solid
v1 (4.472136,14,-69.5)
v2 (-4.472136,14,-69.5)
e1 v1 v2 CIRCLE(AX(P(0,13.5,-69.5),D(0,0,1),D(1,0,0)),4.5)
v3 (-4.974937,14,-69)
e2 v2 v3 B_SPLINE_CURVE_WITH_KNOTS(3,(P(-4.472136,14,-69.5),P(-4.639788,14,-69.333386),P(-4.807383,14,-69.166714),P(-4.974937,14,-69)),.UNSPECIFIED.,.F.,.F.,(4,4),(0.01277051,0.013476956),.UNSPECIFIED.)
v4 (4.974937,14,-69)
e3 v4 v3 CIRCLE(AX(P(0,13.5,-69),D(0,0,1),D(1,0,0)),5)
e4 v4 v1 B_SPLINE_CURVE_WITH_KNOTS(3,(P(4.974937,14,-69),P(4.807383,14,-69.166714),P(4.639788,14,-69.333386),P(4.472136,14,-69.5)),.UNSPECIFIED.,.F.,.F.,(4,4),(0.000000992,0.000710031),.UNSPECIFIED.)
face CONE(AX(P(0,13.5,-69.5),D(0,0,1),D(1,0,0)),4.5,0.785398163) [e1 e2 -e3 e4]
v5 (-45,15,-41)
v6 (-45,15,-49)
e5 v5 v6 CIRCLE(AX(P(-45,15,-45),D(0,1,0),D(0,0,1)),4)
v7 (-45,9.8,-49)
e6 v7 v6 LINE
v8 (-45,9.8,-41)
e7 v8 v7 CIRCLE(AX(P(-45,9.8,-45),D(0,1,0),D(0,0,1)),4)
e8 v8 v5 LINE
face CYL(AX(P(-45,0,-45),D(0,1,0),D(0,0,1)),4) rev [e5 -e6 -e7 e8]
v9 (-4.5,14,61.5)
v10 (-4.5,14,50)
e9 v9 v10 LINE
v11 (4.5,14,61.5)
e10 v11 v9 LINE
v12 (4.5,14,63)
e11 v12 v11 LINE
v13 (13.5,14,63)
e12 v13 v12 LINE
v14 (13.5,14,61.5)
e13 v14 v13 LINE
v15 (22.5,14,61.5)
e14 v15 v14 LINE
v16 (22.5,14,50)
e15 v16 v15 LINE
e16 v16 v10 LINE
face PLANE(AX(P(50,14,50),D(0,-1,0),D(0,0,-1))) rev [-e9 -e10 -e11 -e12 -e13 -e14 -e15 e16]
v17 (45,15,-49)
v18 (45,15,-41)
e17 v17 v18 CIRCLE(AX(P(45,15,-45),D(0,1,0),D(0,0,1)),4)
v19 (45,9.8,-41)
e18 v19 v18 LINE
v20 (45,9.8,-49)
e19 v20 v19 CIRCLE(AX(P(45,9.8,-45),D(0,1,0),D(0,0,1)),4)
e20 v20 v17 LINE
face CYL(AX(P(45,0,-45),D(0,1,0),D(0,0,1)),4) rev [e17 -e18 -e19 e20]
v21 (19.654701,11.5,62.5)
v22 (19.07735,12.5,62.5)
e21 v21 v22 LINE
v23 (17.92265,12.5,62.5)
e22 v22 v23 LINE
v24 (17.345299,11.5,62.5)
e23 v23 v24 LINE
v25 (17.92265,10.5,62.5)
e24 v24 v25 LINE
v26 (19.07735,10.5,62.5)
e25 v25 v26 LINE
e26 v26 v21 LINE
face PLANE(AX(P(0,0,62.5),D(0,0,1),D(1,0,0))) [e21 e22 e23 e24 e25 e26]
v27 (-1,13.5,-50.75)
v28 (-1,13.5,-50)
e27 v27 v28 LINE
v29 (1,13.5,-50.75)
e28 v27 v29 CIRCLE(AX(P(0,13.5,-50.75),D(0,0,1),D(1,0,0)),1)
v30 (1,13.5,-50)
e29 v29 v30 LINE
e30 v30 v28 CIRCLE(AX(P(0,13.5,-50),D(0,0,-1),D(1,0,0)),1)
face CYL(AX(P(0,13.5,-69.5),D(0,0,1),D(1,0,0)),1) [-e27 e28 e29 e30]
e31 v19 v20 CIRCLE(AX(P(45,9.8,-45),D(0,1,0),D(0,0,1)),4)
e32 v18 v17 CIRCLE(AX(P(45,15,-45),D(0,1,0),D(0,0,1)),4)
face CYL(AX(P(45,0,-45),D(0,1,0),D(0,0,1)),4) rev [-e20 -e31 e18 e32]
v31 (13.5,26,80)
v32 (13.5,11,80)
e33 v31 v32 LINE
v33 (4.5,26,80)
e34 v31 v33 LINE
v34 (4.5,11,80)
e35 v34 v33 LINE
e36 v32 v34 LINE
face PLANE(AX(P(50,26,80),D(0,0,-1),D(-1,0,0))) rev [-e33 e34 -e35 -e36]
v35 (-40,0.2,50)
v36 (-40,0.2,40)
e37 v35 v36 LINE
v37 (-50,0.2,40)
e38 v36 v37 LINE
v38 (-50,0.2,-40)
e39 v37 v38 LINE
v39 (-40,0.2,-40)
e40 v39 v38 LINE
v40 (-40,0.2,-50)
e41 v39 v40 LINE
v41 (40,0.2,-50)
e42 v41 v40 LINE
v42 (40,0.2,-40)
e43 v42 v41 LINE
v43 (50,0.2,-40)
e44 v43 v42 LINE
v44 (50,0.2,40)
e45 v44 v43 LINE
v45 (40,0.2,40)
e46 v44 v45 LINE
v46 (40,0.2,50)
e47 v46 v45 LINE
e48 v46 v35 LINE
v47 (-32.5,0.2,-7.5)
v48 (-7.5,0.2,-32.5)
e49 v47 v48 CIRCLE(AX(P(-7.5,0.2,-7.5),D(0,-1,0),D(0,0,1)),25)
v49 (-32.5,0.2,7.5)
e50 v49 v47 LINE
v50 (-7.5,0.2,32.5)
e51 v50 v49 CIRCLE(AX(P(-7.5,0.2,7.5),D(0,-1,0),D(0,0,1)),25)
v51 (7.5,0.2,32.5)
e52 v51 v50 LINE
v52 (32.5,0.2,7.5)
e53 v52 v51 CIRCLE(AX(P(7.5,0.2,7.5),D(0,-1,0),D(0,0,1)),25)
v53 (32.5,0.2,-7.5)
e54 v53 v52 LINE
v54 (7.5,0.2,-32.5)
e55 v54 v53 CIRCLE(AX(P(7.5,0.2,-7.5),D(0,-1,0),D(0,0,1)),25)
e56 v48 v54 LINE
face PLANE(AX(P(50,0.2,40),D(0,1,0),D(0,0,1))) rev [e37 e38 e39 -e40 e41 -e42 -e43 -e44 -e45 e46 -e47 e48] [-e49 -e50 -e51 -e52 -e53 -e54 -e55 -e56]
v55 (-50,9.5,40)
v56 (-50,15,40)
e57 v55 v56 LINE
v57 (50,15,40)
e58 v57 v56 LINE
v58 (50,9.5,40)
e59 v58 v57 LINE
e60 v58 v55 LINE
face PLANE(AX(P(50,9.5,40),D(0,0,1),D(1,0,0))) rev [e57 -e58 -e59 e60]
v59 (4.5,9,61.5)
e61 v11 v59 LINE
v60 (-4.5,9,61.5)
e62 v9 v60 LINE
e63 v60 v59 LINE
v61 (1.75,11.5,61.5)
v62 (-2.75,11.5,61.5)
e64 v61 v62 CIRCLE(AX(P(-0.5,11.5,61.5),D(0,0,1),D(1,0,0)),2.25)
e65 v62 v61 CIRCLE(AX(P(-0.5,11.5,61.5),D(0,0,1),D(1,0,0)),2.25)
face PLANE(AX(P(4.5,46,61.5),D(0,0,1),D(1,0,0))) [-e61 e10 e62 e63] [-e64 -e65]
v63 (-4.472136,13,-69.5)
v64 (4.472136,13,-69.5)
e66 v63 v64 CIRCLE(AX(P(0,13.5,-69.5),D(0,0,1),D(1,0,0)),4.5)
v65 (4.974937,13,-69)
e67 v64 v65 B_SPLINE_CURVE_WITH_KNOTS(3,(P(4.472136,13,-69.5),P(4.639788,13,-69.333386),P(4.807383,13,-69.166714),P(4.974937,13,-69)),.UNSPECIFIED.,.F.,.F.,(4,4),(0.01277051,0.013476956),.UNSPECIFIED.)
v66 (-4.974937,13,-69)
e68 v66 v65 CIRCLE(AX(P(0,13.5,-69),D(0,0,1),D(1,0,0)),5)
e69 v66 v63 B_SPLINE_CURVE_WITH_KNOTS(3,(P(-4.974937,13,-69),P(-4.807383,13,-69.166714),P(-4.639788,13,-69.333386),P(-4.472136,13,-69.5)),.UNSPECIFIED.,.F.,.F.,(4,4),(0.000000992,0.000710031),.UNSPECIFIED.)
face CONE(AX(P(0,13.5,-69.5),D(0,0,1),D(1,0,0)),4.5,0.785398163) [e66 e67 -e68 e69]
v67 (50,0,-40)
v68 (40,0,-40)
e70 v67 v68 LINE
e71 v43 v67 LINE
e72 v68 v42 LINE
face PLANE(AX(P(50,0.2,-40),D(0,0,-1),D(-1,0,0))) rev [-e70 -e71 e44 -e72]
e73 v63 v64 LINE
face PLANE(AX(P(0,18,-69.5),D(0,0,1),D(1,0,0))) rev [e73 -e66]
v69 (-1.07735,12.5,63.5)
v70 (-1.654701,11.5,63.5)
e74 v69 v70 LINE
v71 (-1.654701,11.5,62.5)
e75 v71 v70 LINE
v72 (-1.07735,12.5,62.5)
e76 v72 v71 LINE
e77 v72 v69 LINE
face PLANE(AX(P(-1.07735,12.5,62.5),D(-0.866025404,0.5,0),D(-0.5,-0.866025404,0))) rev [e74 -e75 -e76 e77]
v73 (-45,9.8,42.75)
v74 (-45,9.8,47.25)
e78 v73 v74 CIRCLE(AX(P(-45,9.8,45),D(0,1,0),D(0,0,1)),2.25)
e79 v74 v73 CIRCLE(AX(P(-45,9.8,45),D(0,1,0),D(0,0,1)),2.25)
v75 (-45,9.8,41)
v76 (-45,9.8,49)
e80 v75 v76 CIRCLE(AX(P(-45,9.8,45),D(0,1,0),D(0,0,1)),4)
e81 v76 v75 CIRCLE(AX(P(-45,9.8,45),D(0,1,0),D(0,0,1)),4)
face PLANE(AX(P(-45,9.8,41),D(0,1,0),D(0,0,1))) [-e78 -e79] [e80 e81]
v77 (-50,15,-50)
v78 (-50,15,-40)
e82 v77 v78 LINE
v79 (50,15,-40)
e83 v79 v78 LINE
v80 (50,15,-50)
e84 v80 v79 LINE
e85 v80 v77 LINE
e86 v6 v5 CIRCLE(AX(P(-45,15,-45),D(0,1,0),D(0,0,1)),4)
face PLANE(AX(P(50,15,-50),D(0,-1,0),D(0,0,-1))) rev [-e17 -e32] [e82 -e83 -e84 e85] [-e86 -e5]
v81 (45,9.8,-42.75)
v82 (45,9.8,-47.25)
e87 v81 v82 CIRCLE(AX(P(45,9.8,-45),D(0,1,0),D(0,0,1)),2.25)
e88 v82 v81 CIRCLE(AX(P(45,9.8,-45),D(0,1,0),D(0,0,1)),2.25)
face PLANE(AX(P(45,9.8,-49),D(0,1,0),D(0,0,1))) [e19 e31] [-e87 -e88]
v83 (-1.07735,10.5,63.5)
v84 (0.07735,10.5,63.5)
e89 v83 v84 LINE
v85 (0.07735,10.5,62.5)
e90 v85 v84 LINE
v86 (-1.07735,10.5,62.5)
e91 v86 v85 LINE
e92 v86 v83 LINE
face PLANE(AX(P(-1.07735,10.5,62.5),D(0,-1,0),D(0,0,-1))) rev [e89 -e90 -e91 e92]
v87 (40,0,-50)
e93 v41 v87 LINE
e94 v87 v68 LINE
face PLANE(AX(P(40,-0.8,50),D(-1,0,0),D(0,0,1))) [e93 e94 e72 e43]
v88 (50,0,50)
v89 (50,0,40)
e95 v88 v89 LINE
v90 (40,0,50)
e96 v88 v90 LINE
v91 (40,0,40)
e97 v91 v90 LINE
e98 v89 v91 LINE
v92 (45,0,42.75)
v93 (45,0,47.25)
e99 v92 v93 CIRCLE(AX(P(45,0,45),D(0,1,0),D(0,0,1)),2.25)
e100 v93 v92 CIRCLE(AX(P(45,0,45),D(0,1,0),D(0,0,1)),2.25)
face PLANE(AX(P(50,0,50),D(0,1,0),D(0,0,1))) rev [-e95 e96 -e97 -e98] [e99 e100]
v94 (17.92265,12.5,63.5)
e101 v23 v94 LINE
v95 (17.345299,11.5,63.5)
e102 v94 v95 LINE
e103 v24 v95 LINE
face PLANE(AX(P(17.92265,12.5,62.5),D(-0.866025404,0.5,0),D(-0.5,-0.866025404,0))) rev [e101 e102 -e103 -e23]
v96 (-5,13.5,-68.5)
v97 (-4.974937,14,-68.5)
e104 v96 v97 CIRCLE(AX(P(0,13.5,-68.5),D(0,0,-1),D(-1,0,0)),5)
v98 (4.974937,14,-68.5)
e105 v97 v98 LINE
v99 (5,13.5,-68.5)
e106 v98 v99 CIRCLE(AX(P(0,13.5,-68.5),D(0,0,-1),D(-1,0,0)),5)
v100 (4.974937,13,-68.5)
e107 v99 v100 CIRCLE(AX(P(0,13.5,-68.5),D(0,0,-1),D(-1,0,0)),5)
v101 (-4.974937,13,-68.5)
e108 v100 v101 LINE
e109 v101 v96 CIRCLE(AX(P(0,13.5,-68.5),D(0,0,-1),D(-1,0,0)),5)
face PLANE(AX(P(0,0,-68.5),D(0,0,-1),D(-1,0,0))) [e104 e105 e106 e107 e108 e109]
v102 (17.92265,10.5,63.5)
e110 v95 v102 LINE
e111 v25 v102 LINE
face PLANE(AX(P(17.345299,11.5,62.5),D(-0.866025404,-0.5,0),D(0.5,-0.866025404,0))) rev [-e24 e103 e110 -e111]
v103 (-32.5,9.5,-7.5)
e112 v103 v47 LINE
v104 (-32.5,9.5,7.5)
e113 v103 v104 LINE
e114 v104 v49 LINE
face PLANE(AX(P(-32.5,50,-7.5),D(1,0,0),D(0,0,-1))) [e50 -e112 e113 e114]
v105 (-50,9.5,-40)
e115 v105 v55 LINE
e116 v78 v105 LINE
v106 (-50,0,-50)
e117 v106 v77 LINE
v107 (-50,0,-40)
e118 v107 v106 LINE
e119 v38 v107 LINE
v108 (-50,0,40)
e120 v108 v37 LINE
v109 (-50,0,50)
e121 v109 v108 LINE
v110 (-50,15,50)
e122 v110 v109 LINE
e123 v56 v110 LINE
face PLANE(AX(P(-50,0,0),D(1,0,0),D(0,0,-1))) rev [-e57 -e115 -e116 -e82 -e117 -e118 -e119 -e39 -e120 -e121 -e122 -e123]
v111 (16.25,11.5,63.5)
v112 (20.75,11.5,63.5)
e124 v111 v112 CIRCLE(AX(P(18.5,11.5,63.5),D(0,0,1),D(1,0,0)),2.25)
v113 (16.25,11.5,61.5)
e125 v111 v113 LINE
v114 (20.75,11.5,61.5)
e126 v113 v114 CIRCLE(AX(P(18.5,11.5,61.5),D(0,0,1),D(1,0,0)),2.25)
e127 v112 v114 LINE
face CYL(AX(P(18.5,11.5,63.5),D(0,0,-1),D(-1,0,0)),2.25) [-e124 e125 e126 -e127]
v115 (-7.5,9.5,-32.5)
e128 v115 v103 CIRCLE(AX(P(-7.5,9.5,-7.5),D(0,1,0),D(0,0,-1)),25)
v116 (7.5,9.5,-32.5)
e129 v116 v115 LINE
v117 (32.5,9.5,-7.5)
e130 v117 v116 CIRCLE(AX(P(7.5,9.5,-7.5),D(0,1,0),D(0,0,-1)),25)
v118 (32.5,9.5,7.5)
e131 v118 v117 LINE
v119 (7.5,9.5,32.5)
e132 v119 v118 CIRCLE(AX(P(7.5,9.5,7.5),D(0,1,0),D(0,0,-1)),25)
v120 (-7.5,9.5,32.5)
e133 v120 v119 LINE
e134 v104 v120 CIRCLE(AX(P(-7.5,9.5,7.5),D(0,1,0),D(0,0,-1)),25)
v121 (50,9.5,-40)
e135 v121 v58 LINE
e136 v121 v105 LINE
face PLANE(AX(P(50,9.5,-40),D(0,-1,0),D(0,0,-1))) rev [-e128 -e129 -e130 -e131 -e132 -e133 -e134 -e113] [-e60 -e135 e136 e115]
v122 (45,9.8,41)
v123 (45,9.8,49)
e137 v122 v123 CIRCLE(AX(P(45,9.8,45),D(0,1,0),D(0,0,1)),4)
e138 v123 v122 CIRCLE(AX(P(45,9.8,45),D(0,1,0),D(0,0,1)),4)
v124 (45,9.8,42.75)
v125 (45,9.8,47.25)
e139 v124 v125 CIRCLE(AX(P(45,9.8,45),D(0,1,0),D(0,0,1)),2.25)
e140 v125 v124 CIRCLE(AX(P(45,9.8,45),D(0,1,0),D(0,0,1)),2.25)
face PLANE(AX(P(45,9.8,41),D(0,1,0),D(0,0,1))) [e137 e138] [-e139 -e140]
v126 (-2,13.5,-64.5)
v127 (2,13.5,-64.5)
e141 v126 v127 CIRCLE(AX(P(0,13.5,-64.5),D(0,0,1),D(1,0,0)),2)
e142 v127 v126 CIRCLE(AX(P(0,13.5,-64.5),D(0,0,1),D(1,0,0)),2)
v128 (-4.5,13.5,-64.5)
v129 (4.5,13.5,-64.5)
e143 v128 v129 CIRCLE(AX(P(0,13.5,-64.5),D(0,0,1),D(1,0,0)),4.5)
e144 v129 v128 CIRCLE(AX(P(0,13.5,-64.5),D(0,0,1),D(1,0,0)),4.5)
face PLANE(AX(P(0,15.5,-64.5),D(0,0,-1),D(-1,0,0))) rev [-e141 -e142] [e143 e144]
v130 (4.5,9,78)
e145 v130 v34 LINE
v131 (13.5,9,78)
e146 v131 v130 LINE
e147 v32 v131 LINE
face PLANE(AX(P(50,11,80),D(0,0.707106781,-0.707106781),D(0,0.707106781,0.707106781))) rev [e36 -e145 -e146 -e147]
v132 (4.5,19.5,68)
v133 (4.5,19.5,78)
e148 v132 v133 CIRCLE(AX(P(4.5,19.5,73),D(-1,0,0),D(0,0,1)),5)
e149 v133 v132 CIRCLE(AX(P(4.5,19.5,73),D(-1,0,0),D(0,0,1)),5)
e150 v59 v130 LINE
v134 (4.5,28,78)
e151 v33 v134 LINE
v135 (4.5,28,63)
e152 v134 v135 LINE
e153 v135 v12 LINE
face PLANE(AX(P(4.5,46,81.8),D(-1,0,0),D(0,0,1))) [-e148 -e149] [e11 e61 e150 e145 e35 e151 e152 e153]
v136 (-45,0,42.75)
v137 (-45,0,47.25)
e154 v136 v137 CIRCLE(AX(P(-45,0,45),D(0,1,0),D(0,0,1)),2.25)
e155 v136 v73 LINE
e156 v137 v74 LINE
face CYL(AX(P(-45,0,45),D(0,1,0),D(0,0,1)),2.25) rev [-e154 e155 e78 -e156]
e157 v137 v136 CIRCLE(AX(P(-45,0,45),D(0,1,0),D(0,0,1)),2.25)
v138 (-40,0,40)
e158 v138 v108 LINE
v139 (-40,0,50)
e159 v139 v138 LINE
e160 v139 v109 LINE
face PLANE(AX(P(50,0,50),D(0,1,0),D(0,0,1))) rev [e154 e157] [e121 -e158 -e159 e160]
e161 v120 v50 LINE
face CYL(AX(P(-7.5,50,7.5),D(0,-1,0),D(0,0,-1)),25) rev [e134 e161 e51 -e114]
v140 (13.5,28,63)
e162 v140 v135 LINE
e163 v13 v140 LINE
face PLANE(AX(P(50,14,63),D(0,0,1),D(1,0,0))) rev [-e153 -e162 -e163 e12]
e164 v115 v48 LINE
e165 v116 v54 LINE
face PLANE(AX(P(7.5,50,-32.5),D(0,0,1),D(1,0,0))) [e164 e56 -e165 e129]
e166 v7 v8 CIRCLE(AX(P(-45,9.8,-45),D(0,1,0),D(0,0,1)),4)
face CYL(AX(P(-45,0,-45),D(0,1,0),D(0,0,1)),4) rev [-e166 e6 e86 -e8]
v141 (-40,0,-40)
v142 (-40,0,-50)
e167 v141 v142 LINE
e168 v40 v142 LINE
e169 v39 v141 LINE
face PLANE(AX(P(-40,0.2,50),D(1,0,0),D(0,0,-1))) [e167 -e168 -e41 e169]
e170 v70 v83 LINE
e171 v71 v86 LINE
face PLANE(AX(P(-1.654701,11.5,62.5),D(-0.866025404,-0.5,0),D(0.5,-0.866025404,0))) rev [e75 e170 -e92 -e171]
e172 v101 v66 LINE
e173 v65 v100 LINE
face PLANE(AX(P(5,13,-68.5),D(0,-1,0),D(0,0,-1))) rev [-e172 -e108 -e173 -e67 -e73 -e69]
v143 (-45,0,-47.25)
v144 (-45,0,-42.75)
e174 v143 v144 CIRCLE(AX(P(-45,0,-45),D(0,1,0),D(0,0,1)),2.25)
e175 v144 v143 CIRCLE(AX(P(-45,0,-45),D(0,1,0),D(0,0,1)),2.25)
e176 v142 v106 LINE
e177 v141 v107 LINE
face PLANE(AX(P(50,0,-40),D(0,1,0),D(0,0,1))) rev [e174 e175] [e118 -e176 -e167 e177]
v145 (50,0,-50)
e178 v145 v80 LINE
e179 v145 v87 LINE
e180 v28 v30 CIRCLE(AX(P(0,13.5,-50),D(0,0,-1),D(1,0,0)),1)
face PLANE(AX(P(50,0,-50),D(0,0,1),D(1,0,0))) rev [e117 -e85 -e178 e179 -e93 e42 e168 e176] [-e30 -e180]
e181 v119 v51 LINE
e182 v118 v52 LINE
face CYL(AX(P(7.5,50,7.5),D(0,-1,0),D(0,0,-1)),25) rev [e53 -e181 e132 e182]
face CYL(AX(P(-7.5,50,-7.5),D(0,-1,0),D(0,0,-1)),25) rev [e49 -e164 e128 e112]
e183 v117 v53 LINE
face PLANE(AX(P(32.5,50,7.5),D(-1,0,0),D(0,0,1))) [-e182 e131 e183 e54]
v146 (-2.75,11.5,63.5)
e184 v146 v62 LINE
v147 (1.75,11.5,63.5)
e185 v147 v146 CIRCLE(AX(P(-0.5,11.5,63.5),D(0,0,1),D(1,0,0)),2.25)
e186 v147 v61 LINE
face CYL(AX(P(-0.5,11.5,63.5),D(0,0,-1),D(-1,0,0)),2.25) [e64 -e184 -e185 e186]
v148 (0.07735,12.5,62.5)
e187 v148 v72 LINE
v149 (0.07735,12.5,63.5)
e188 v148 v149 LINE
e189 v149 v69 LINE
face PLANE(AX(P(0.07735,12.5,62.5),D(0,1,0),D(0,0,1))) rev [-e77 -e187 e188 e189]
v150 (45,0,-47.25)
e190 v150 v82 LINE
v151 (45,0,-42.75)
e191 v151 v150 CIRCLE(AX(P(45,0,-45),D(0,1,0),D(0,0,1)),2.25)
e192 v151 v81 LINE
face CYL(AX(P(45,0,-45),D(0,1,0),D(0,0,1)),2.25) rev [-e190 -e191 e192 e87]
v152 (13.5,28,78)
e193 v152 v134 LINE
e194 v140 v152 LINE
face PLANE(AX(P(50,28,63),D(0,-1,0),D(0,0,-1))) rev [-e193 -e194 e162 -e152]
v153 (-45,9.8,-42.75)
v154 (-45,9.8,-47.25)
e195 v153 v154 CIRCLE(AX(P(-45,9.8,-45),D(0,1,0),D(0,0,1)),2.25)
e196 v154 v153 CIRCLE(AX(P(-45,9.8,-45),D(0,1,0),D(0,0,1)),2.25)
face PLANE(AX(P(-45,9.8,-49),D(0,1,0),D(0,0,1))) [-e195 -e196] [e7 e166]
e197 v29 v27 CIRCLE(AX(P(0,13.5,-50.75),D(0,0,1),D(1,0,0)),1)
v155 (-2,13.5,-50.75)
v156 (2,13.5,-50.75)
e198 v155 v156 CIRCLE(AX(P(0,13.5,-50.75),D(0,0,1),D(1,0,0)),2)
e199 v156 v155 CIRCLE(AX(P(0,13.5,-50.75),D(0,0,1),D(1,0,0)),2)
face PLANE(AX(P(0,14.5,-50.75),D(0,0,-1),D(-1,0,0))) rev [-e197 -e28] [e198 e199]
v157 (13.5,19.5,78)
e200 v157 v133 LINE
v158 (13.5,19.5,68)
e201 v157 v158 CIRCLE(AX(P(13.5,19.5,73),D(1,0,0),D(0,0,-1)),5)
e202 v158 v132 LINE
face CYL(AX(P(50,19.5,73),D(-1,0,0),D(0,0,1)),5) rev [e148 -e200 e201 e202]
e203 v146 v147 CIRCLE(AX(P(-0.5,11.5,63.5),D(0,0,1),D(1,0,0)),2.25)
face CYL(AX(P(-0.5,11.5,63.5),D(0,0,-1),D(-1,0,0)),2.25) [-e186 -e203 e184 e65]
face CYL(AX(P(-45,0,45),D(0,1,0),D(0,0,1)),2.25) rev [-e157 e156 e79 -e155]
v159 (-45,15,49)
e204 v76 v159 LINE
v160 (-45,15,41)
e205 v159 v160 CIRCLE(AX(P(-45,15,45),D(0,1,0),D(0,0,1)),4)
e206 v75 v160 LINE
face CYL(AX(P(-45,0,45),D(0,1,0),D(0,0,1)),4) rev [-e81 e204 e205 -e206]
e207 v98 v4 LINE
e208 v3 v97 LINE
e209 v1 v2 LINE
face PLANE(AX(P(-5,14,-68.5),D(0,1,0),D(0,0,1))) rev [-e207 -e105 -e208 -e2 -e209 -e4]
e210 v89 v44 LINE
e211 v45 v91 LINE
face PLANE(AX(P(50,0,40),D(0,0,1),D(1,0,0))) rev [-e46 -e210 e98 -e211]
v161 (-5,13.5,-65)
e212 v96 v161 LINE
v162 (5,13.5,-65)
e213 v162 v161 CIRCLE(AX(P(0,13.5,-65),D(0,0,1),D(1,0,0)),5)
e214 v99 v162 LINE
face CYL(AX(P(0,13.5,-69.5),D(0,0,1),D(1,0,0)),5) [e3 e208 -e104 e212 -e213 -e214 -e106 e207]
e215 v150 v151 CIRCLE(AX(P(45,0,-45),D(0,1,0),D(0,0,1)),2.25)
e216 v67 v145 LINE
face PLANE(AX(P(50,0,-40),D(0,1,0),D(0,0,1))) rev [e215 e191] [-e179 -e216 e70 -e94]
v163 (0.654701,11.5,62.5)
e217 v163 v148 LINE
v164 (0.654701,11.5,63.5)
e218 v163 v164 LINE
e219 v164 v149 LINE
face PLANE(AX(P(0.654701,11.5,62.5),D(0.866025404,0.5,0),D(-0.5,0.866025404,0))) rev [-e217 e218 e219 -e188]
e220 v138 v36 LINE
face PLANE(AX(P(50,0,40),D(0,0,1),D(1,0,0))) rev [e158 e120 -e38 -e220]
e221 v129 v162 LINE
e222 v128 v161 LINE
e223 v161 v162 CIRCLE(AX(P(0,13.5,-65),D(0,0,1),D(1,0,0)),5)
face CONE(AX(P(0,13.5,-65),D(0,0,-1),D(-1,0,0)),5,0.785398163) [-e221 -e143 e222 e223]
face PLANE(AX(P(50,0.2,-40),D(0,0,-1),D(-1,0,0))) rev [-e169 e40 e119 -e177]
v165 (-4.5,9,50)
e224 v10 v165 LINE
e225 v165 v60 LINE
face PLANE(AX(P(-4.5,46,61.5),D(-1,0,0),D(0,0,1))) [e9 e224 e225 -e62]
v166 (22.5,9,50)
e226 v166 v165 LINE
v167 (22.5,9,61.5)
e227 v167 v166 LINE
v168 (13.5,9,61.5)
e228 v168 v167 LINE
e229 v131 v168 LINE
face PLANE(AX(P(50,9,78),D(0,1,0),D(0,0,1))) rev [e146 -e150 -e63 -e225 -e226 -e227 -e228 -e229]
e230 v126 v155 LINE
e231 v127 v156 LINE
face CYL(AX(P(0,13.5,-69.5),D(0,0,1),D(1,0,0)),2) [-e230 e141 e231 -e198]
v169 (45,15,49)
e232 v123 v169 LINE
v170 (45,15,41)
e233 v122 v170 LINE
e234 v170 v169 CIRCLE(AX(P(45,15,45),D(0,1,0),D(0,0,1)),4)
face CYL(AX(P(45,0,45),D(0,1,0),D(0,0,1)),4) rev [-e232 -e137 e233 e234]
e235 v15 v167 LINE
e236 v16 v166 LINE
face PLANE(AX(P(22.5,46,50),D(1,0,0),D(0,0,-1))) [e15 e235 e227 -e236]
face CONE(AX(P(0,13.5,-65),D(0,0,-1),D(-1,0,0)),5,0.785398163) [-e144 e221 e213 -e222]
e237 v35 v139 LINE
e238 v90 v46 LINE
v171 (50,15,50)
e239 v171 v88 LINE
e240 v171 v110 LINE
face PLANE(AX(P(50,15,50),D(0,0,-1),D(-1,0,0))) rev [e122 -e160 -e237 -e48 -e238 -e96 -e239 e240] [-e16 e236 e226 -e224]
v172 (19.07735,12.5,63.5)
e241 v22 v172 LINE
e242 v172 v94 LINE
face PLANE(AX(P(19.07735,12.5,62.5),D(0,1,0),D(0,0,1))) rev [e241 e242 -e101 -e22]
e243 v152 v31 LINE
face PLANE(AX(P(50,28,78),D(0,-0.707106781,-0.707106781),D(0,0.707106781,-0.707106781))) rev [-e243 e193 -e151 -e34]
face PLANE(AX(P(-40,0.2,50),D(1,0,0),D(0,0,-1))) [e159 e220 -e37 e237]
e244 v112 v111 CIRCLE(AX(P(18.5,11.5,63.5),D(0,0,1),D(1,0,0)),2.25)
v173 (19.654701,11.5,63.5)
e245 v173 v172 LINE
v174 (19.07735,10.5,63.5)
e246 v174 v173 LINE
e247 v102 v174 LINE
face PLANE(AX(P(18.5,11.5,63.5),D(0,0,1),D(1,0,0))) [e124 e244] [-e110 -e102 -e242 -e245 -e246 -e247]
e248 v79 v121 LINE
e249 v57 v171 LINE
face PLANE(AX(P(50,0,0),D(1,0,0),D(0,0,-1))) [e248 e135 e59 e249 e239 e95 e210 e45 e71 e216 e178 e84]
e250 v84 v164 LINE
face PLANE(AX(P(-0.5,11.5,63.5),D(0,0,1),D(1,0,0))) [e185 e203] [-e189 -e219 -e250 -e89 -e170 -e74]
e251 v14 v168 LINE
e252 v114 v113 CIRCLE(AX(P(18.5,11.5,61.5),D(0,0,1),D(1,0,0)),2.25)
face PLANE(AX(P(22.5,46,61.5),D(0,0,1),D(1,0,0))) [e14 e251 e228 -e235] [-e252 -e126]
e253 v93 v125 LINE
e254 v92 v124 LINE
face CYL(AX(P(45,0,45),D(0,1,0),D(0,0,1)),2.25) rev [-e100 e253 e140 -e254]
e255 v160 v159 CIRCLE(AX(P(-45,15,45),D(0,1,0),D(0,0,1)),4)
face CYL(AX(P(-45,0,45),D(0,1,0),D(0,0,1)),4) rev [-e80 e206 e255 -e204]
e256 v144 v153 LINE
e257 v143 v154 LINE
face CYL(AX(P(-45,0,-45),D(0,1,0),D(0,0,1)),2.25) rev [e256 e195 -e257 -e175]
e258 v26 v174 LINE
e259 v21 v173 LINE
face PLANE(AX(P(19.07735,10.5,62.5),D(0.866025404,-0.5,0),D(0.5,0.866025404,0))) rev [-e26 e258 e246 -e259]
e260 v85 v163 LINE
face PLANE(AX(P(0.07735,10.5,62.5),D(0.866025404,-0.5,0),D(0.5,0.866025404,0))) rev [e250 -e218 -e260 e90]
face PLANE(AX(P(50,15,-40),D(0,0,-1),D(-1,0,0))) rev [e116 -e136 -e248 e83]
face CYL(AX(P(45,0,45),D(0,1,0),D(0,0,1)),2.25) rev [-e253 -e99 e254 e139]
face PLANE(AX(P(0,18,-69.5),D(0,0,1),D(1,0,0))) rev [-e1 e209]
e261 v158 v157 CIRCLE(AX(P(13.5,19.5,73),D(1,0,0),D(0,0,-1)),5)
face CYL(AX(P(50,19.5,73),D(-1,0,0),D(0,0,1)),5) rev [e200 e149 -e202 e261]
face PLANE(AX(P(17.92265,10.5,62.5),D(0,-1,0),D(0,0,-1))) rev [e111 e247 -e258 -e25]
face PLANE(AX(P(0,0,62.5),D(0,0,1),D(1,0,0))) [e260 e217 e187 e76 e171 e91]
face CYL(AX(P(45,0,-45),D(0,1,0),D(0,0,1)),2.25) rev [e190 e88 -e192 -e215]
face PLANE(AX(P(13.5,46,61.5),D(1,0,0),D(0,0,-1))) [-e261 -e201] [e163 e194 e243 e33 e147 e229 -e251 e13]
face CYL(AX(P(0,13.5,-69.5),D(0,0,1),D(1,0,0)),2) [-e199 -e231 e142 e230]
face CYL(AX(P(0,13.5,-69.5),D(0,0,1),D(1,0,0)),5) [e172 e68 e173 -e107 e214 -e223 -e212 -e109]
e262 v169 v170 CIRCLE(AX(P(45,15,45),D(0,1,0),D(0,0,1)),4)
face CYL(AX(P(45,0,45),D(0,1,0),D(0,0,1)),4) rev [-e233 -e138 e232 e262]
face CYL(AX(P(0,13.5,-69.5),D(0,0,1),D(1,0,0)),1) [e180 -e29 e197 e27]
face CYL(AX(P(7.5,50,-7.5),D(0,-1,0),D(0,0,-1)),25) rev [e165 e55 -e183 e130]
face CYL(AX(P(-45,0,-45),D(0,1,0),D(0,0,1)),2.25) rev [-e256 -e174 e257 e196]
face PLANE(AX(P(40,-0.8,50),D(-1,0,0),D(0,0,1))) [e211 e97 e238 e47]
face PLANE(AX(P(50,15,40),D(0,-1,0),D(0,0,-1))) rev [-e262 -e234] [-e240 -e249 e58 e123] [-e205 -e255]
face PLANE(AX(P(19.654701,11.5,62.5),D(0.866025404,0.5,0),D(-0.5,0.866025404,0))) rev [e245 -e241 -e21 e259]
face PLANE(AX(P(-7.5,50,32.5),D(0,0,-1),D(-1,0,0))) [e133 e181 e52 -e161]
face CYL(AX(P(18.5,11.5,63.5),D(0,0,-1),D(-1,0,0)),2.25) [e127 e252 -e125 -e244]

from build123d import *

# Parameters (mm, degrees)
EXTRUDE_1_DEPTH          = 50
EXTRUDE_1_DEPTH_BACK     = 50
CUT_EXTRUDE_1_DEPTH      = 50
CUT_EXTRUDE_1_DEPTH_BACK = 50
SKETCH_2_W               = 80
SKETCH_2_H               = 1
EXTRUDE_2_DEPTH          = 50
EXTRUDE_2_DEPTH_BACK     = 50
SKETCH_7_R               = 5
CUT_EXTRUDE_2_DEPTH      = 45
CUT_EXTRUDE_3_DEPTH      = 50
SKETCH_11_W              = 10
SKETCH_11_H              = 1
CUT_EXTRUDE_4_DEPTH      = 1
SKETCH_12_R              = 2.25
EXTRUDE_3_DEPTH          = 2
SKETCH_13_R              = 2.25
EXTRUDE_4_DEPTH          = 2
CUT_EXTRUDE_5_DEPTH      = 1
CUT_EXTRUDE_6_DEPTH      = 1


with BuildPart() as part:
    # 草图1 → 凸台-拉伸1 (new, two sides: drawn at the far end of the back side and taken through both)
    with BuildSketch(Plane(origin=(0, 0, 0), x_dir=(0, 0, -1), z_dir=(1, 0, 0)).offset(-EXTRUDE_1_DEPTH_BACK)):
        Polygon((-50, 15), (-50, 0), (-40, 0), (-40, 0.2), (40, 0.2), (40, 0), (50, 0), (50, 15), (40, 15), (40, 9.5), (-40, 9.5), (-40, 15), align=None)
    extrude(amount=EXTRUDE_1_DEPTH + EXTRUDE_1_DEPTH_BACK)

    # 草图2 → 切除-拉伸1 (cut, two sides: drawn at the far end of the back side and taken through both)
    with BuildSketch(Plane.XY.offset(-CUT_EXTRUDE_1_DEPTH_BACK)):
        with Locations((0, -0.3)):
            Rectangle(SKETCH_2_W, SKETCH_2_H)
    extrude(amount=CUT_EXTRUDE_1_DEPTH + CUT_EXTRUDE_1_DEPTH_BACK, mode=Mode.SUBTRACT)

    # 草图3 → 切除-旋转1 (revolve, cut)
    with BuildSketch(Plane(origin=(45, 0, 0), x_dir=(0, 0, -1), z_dir=(1, 0, 0)), mode=Mode.PRIVATE) as cut_revolve_1_sk:
        Polygon((-45, 15), (-41, 15), (-41, 9.8), (-42.75, 9.8), (-42.75, 0), (-45, 0), align=None)
    revolve(cut_revolve_1_sk.sketch.rotate(Axis((45, 0, 45), (0, 1, 0)), 180), axis=Axis((45, 0, 45), (0, 1, 0)), mode=Mode.SUBTRACT)

    # 草图4 → 切除-旋转2 (revolve, cut)
    with BuildSketch(Plane(origin=(-45, 0, 0), x_dir=(0, 0, -1), z_dir=(1, 0, 0)), mode=Mode.PRIVATE) as cut_revolve_2_sk:
        Polygon((-45, 15), (-41, 15), (-41, 9.8), (-42.75, 9.8), (-42.75, 0), (-45, 0), align=None)
    revolve(cut_revolve_2_sk.sketch.rotate(Axis((-45, 0, 45), (0, 1, 0)), 180), axis=Axis((-45, 0, 45), (0, 1, 0)), mode=Mode.SUBTRACT)

    # 草图5 → 切除-旋转3 (revolve, cut)
    with BuildSketch(Plane(origin=(-45, 0, 0), x_dir=(0, 0, -1), z_dir=(1, 0, 0)), mode=Mode.PRIVATE) as cut_revolve_3_sk:
        Polygon((45, 15), (49, 15), (49, 9.8), (47.25, 9.8), (47.25, 0), (45, 0), align=None)
    revolve(cut_revolve_3_sk.sketch.rotate(Axis((-45, 0, -45), (0, 1, 0)), 180), axis=Axis((-45, 0, -45), (0, 1, 0)), mode=Mode.SUBTRACT)

    # 草图6 → 切除-旋转4 (revolve, cut)
    with BuildSketch(Plane(origin=(45, 0, 0), x_dir=(0, 0, -1), z_dir=(1, 0, 0)), mode=Mode.PRIVATE) as cut_revolve_4_sk:
        Polygon((45, 15), (49, 15), (49, 9.8), (47.25, 9.8), (47.25, 0), (45, 0), align=None)
    revolve(cut_revolve_4_sk.sketch.rotate(Axis((45, 0, -45), (0, 1, 0)), 180), axis=Axis((45, 0, -45), (0, 1, 0)), mode=Mode.SUBTRACT)

    # 草图7 → 凸台-拉伸2 (add, two sides: drawn at the far end of the back side and taken through both)
    with BuildSketch(Plane(origin=(0, 0, 0), x_dir=(0, 0, -1), z_dir=(1, 0, 0)).offset(-EXTRUDE_2_DEPTH_BACK)):
        Polygon((-80, 26), (-80, 11), (-78, 9), (-50, 9), (-50, 14), (-63, 14), (-63, 28), (-78, 28), align=None)
        with Locations((-73, 19.5)):
            Circle(SKETCH_7_R, mode=Mode.SUBTRACT)
    extrude(amount=EXTRUDE_2_DEPTH + EXTRUDE_2_DEPTH_BACK)

    # 草图8 → 切除-拉伸2 (cut)
    with BuildSketch(Plane(origin=(0, 1, 0), x_dir=(-1, 0, 0), z_dir=(0, 1, 0))):
        Polygon((50, 84.5), (-50, 84.5), (-50, 50), (-22.5, 50), (-22.5, 61.5), (-13.5, 61.5), (-13.5, 81.8), (-4.5, 81.8), (-4.5, 61.5), (4.5, 61.5), (4.5, 50), (50, 50), align=None)
    extrude(amount=CUT_EXTRUDE_2_DEPTH, mode=Mode.SUBTRACT)

    # 草图9 → 旋转1 (revolve)
    with BuildSketch(Plane(origin=(0, 0, 0), x_dir=(0, 0, -1), z_dir=(1, 0, 0)), mode=Mode.PRIVATE) as revolve_1_sk:
        Polygon((50, 13.5), (50, 14.5), (50.75, 14.5), (50.75, 15.5), (64.5, 15.5), (64.5, 18), (65, 18.5), (69, 18.5), (69.5, 18), (69.5, 13.5), align=None)
    revolve(revolve_1_sk.sketch.rotate(Axis((0, 13.5, -69.5), (0, 0, 1)), 270), axis=Axis((0, 13.5, -69.5), (0, 0, 1)))

    # 草图10 → 切除-拉伸3 (cut)
    with BuildSketch(Plane(origin=(0, 0, 0), x_dir=(-1, 0, 0), z_dir=(0, 1, 0))):
        with BuildLine():
            Line((7.5, 32.5), (-7.5, 32.5))
            ThreePointArc((-7.5, 32.5), (-25.17766953, 25.17766953), (-32.5, 7.5))
            Line((-32.5, 7.5), (-32.5, -7.5))
            ThreePointArc((-32.5, -7.5), (-25.17766953, -25.17766953), (-7.5, -32.5))
            Line((-7.5, -32.5), (7.5, -32.5))
            ThreePointArc((7.5, -32.5), (25.17766953, -25.17766953), (32.5, -7.5))
            Line((32.5, -7.5), (32.5, 7.5))
            ThreePointArc((32.5, 7.5), (25.17766953, 25.17766953), (7.5, 32.5))
        make_face()
    extrude(amount=CUT_EXTRUDE_3_DEPTH, mode=Mode.SUBTRACT)

    # 草图11 → 切除-拉伸4 (cut)
    with BuildSketch(Plane(origin=(0, 0, -69.5), x_dir=(-1, 0, 0), z_dir=(0, 0, -1))):
        with Locations((0, 13.5)):
            Rectangle(SKETCH_11_W, SKETCH_11_H)
    extrude(amount=-CUT_EXTRUDE_4_DEPTH, mode=Mode.SUBTRACT)

    # 草图12 → 凸台-拉伸3 (add)
    with BuildSketch(Plane.XY.offset(61.5)):
        with Locations((-0.5, 11.5)):
            Circle(SKETCH_12_R)
    extrude(amount=EXTRUDE_3_DEPTH)

    # 草图13 → 凸台-拉伸4 (add)
    with BuildSketch(Plane.XY.offset(61.5)):
        with Locations((18.5, 11.5)):
            Circle(SKETCH_13_R)
    extrude(amount=EXTRUDE_4_DEPTH)

    # 草图14 → 切除-拉伸5 (cut)
    with BuildSketch(Plane.XY.offset(63.5)):
        Polygon((-1.077350269, 12.5), (-1.654700538, 11.5), (-1.077350269, 10.5), (0.077350269, 10.5), (0.654700538, 11.5), (0.077350269, 12.5), align=None)
    extrude(amount=-CUT_EXTRUDE_5_DEPTH, mode=Mode.SUBTRACT)

    # 草图15 → 切除-拉伸6 (cut)
    with BuildSketch(Plane.XY.offset(63.5)):
        Polygon((17.922649731, 12.5), (17.345299462, 11.5), (17.922649731, 10.5), (19.077350269, 10.5), (19.654700538, 11.5), (19.077350269, 12.5), align=None)
    extrude(amount=-CUT_EXTRUDE_6_DEPTH, mode=Mode.SUBTRACT)


solid = part.part
